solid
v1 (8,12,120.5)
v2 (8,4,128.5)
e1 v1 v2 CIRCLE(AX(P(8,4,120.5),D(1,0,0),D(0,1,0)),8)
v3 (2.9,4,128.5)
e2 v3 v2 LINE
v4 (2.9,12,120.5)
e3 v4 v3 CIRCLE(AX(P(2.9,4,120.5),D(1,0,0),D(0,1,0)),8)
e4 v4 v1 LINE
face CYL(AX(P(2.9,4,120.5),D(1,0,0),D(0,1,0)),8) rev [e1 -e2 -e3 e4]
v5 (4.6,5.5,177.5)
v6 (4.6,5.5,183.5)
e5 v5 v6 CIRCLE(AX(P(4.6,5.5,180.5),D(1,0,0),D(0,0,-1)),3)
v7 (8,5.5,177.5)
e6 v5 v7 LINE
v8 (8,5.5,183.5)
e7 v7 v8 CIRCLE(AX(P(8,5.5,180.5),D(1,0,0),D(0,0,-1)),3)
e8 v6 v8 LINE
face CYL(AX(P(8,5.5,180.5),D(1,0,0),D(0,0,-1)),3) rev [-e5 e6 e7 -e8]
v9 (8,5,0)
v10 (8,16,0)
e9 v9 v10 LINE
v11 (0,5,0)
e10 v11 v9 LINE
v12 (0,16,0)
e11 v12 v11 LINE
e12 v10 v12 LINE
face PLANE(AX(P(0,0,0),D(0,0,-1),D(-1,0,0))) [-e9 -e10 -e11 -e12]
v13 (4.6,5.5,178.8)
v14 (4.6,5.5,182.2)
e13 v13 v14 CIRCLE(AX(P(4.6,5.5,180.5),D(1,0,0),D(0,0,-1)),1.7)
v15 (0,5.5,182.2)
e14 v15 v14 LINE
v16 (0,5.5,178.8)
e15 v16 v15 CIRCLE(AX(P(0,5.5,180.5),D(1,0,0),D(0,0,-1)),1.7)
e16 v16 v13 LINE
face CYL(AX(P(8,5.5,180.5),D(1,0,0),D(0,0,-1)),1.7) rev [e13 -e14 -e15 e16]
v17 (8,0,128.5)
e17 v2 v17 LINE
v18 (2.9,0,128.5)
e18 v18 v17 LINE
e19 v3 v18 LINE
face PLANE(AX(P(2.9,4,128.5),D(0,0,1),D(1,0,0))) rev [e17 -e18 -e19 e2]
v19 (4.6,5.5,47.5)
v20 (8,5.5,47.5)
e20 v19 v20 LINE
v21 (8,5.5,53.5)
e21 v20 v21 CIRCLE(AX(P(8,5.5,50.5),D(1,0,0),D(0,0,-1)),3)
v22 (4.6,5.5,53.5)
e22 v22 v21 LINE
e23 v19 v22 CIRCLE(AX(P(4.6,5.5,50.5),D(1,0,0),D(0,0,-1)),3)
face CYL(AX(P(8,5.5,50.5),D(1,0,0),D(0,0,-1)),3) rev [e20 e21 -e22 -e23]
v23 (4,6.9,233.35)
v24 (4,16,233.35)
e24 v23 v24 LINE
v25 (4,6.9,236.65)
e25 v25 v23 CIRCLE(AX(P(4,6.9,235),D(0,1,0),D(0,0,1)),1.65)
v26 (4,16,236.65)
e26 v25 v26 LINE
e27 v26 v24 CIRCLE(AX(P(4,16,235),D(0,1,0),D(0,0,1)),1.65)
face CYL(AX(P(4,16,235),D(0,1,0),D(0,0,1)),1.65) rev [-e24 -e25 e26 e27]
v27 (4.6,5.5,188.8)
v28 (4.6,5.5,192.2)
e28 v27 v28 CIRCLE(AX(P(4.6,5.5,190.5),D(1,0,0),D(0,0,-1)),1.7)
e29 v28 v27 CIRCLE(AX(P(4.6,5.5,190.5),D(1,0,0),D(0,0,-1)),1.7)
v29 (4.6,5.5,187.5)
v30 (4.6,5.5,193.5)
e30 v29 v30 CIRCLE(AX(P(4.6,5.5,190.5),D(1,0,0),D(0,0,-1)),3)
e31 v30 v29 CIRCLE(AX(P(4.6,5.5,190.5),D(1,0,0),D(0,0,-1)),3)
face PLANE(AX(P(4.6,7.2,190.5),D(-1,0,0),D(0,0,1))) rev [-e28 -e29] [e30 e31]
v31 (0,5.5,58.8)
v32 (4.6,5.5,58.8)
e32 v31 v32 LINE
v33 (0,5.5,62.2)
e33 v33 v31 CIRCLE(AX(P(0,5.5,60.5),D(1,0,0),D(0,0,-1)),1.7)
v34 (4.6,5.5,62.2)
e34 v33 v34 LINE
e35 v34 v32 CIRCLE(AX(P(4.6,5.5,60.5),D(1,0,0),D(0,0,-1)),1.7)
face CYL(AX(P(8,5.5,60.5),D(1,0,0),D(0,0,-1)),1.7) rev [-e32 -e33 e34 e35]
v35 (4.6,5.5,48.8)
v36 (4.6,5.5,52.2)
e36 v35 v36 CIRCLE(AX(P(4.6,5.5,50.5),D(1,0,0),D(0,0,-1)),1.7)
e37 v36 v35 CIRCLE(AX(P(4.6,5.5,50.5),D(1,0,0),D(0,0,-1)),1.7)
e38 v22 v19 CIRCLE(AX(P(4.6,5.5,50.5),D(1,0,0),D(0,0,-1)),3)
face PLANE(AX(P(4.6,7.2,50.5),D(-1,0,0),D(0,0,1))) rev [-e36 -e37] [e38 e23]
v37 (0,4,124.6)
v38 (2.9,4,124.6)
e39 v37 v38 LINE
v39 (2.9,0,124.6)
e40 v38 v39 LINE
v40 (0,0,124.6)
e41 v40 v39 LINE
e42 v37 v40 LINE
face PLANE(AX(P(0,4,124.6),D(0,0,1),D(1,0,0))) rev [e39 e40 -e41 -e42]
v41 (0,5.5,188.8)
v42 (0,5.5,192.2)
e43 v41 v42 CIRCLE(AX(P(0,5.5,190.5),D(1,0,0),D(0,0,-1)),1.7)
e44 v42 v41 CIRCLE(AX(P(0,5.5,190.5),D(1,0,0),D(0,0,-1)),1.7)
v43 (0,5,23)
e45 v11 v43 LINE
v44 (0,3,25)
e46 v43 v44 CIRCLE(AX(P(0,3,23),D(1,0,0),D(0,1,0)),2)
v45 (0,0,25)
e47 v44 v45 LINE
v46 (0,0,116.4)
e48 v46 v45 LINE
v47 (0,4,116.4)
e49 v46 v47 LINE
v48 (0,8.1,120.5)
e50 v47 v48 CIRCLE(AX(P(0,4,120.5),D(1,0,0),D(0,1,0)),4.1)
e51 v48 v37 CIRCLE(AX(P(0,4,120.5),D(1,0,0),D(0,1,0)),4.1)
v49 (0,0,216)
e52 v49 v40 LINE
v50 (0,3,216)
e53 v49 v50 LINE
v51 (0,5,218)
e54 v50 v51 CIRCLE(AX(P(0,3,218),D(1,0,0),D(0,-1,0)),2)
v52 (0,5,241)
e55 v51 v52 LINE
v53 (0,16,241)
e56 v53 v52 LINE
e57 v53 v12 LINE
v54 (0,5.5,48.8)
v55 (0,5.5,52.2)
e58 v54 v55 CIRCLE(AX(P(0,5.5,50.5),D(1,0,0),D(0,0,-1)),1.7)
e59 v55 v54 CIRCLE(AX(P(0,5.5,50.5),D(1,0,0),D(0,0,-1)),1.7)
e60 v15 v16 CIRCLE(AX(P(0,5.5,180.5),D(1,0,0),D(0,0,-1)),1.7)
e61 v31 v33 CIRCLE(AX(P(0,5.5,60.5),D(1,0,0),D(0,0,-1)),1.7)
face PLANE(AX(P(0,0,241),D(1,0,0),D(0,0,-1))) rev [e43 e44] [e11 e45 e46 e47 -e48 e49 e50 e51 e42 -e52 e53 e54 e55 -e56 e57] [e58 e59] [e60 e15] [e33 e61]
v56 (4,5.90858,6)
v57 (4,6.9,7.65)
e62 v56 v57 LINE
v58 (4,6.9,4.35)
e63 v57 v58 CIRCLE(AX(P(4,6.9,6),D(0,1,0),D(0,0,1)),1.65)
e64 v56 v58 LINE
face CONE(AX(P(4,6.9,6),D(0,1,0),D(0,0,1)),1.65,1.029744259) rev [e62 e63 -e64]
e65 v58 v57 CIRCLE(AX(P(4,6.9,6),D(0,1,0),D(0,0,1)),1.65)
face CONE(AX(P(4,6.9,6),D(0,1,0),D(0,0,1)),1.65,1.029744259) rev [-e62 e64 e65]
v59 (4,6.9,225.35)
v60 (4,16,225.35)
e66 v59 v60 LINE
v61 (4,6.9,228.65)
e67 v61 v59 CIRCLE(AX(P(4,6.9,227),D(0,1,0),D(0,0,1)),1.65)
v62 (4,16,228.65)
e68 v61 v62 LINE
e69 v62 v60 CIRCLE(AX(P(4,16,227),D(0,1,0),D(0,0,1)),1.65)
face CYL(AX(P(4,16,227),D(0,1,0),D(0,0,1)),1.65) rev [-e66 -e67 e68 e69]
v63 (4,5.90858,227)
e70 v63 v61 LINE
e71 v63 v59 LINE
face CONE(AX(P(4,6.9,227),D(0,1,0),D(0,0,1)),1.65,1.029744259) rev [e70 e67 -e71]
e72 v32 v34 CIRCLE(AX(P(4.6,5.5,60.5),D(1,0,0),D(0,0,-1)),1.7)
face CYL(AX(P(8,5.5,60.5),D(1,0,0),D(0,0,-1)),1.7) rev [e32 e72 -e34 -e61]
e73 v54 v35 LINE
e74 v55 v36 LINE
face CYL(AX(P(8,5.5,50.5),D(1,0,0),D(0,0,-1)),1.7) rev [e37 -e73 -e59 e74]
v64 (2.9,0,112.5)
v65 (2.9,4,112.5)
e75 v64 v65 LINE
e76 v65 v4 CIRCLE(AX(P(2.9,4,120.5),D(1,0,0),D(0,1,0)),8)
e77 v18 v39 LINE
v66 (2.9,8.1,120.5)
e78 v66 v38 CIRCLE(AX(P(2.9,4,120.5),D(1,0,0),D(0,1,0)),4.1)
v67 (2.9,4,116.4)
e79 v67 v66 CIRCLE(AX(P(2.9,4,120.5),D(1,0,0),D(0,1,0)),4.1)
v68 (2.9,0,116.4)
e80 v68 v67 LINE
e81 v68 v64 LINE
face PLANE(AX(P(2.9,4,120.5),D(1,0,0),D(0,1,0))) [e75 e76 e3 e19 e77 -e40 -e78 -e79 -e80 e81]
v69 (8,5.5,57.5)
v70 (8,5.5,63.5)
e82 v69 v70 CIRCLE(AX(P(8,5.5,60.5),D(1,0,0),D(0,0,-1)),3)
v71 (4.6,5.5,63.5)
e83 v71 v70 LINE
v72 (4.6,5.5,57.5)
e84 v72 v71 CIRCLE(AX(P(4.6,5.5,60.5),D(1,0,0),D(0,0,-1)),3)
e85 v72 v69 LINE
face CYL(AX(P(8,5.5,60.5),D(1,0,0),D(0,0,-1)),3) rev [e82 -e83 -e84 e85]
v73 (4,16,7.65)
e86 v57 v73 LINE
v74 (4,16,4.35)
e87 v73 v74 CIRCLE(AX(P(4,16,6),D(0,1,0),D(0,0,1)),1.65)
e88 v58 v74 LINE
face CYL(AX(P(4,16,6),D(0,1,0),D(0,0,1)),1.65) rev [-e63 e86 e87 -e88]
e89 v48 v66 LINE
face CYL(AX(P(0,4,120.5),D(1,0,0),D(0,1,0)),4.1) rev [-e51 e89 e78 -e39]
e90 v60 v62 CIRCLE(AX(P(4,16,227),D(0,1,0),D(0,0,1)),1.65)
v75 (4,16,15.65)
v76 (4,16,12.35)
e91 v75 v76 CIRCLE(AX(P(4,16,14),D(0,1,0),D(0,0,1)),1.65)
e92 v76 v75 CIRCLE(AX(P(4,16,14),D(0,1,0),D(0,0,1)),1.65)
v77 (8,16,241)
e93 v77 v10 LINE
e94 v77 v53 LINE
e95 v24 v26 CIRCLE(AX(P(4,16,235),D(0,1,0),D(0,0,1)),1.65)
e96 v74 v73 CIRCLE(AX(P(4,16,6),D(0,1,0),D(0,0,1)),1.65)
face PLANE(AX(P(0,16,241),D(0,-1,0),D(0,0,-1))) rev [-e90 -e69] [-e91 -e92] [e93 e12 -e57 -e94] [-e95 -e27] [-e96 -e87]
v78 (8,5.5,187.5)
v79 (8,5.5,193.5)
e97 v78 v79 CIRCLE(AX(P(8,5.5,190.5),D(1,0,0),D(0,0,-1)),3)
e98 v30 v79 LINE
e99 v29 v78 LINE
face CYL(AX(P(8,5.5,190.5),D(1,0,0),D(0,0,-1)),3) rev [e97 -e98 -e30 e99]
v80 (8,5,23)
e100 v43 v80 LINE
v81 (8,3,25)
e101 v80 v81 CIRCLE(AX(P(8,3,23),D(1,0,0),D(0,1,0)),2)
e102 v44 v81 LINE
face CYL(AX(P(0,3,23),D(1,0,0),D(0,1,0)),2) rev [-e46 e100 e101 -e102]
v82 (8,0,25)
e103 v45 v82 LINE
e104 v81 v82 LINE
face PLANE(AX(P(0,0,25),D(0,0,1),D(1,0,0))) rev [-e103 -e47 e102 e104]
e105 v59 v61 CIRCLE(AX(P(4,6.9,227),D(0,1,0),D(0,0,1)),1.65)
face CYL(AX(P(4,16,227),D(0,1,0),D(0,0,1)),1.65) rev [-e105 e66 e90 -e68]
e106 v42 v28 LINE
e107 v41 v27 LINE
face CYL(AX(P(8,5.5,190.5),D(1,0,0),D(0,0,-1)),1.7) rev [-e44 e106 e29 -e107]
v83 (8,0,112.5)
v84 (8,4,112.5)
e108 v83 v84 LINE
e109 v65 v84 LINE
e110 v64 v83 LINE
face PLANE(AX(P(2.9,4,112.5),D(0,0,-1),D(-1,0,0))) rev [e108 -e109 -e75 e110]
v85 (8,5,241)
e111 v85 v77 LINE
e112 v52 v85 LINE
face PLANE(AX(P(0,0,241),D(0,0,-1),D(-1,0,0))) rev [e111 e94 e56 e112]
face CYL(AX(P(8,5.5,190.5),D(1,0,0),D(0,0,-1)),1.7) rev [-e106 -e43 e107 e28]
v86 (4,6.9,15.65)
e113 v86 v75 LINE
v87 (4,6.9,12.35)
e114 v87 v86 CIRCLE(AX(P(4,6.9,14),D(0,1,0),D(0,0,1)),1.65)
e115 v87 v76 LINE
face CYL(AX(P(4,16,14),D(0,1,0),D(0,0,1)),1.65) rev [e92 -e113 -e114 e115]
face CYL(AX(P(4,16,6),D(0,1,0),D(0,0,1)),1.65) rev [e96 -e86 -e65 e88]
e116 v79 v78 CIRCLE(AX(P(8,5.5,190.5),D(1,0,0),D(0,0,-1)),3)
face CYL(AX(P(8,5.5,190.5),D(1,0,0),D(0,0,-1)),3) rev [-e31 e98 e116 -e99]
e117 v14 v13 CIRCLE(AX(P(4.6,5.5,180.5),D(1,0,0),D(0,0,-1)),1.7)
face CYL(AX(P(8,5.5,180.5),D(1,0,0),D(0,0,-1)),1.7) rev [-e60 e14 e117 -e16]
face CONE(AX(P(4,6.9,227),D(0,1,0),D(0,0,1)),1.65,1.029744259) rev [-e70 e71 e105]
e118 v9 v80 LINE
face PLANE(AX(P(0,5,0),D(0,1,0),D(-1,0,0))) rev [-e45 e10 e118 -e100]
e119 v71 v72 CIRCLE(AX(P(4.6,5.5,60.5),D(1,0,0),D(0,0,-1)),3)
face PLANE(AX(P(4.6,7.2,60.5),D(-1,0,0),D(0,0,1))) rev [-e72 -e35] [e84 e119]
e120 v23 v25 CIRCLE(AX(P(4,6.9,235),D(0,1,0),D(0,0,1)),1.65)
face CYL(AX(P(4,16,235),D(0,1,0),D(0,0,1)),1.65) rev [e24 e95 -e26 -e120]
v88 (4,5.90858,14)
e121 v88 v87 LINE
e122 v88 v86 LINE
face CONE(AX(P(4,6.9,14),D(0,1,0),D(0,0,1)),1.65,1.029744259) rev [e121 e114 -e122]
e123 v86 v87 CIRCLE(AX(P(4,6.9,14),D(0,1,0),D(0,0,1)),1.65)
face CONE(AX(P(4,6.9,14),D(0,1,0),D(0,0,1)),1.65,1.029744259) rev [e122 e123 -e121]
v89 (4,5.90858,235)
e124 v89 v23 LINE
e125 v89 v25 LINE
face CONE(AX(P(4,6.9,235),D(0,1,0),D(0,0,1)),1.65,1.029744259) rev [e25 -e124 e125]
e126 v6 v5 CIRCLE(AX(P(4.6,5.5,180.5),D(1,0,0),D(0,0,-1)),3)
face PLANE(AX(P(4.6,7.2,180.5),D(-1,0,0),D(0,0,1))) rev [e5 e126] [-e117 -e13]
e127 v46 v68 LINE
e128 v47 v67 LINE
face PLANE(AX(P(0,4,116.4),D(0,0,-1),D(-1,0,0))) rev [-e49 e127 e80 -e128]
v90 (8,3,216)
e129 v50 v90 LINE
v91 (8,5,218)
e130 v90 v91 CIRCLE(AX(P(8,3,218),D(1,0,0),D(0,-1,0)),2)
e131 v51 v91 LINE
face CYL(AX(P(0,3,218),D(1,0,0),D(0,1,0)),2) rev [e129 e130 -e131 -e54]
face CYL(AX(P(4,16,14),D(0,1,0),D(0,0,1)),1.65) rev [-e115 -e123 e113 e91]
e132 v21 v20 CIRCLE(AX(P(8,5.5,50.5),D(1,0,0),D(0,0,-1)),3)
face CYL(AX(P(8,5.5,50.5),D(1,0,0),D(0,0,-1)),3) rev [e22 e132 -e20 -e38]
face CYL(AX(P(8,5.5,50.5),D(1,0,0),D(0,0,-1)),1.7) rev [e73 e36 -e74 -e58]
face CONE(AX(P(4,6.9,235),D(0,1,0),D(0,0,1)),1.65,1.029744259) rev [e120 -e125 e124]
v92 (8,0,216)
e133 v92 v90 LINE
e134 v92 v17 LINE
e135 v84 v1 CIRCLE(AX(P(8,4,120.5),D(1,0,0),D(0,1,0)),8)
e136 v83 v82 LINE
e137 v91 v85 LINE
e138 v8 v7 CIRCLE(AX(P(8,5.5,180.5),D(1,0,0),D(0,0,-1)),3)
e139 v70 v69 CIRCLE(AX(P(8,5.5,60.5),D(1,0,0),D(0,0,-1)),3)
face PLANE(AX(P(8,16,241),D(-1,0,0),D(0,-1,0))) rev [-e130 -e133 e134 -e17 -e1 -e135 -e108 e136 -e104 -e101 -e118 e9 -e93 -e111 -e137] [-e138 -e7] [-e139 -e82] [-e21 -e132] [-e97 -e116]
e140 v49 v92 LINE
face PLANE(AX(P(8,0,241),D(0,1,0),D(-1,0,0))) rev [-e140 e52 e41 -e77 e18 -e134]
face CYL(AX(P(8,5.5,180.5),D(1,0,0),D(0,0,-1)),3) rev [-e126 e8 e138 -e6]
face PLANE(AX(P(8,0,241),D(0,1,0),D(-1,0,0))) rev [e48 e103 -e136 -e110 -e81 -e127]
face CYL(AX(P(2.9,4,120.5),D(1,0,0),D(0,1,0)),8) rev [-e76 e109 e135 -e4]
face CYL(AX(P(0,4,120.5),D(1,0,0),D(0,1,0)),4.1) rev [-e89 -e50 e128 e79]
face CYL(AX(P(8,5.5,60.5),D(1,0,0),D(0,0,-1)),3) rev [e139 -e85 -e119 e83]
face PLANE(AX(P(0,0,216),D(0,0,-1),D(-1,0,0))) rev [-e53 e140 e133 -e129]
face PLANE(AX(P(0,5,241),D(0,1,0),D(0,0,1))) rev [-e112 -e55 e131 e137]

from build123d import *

# Parameters (mm, degrees)
SKETCH3_W                                            = 8
SKETCH3_H                                            = 16
BOSS_EXTRUDE2_DEPTH                                  = 241
CUT_EXTRUDE1_DEPTH                                   = 5.1
CUT_EXTRUDE2_DEPTH                                   = 242.584374495
CBORE_FOR_M3_HEXAGON_SOCKET_HEAD_CAP_SCR_D           = 3.4
CBORE_FOR_M3_HEXAGON_SOCKET_HEAD_CAP_SCR_DEPTH       = 10.1
CBORE_FOR_M3_HEXAGON_SOCKET_HEAD_CAP_SCR_CBORE_D     = 6
CBORE_FOR_M3_HEXAGON_SOCKET_HEAD_CAP_SCR_CBORE_DEPTH = 3.4
CBORE_FOR_M3_HEXAGON_SOCKET_HEAD_CAP_SCR_TIP         = 1.021463052
M4_TAPPED_HOLE1_D                                    = 3.3
M4_TAPPED_HOLE1_DEPTH                                = 9.1
M4_TAPPED_HOLE1_TIP                                  = 0.991420021
CUT_EXTRUDE3_DEPTH                                   = 242.662988478


with BuildPart() as part:
    # Sketch3 → Boss-Extrude2 (new body)
    with BuildSketch(Plane.XY):
        with Locations((4, 8)):
            Rectangle(SKETCH3_W, SKETCH3_H)
    extrude(amount=BOSS_EXTRUDE2_DEPTH)

    # Sketch4 → Cut-Extrude1 (cut)
    with BuildSketch(Plane(origin=(8, 0, 0), x_dir=(0, 0, -1), z_dir=(1, 0, 0))):
        with BuildLine():
            Line((-112.5, 4), (-112.5, 0))
            ThreePointArc((-112.5, 0), (-120.5, -8), (-128.5, 0))
            Line((-128.5, 0), (-128.5, 4))
            ThreePointArc((-128.5, 4), (-120.5, 12), (-112.5, 4))
        make_face()
    extrude(amount=-CUT_EXTRUDE1_DEPTH, mode=Mode.SUBTRACT)

    # Sketch5 → Cut-Extrude2 (cut, through all)
    with BuildSketch(Plane(origin=(2.9, 0, 0), x_dir=(0, 0, -1), z_dir=(1, 0, 0))):
        with BuildLine():
            Line((-116.4, 4), (-116.4, 0))
            ThreePointArc((-116.4, 0), (-120.5, -4.1), (-124.6, 0))
            Line((-124.6, 0), (-124.6, 4))
            ThreePointArc((-124.6, 4), (-120.5, 8.1), (-116.4, 4))
        make_face()
    extrude(amount=-CUT_EXTRUDE2_DEPTH, mode=Mode.SUBTRACT)

    # CBORE for M3 Hexagon socket head cap screws1
    with Locations(Plane(origin=(8, 0, 0), x_dir=(0, 0, -1), z_dir=(1, 0, 0))):
        with Locations((-60.5, 5.5), (-50.5, 5.5), (-190.5, 5.5), (-180.5, 5.5)):
            CounterBoreHole(CBORE_FOR_M3_HEXAGON_SOCKET_HEAD_CAP_SCR_D / 2, CBORE_FOR_M3_HEXAGON_SOCKET_HEAD_CAP_SCR_CBORE_D / 2, CBORE_FOR_M3_HEXAGON_SOCKET_HEAD_CAP_SCR_CBORE_DEPTH, depth=CBORE_FOR_M3_HEXAGON_SOCKET_HEAD_CAP_SCR_DEPTH)
            with Locations((0, 0, -(CBORE_FOR_M3_HEXAGON_SOCKET_HEAD_CAP_SCR_DEPTH + CBORE_FOR_M3_HEXAGON_SOCKET_HEAD_CAP_SCR_TIP / 2))):  # 118° drill point
                Cone(0, CBORE_FOR_M3_HEXAGON_SOCKET_HEAD_CAP_SCR_D / 2, CBORE_FOR_M3_HEXAGON_SOCKET_HEAD_CAP_SCR_TIP, mode=Mode.SUBTRACT)

    # M4 Tapped Hole1
    with Locations(Plane(origin=(0, 16, 0), x_dir=(1, 0, 0), z_dir=(0, 1, 0))):
        with Locations((4, -235), (4, -227), (4, -14), (4, -6)):
            Hole(M4_TAPPED_HOLE1_D / 2, depth=M4_TAPPED_HOLE1_DEPTH)
            with Locations((0, 0, -(M4_TAPPED_HOLE1_DEPTH + M4_TAPPED_HOLE1_TIP / 2))):  # 118° drill point
                Cone(0, M4_TAPPED_HOLE1_D / 2, M4_TAPPED_HOLE1_TIP, mode=Mode.SUBTRACT)

    # Sketch10 → Cut-Extrude3 (cut, through all)
    with BuildSketch(Plane(origin=(8, 0, 0), x_dir=(0, 0, -1), z_dir=(1, 0, 0))):
        with BuildLine():
            Line((0, 0), (-25, 0))
            Line((-25, 0), (-25, 3))
            ThreePointArc((-25, 3), (-24.414213562, 4.414213562), (-23, 5))
            Line((-23, 5), (0, 5))
            Line((0, 5), (0, 0))
        make_face()
        with BuildLine():
            Line((-216, 0), (-216, 3))
            ThreePointArc((-216, 3), (-216.585786438, 4.414213562), (-218, 5))
            Line((-218, 5), (-241, 5))
            Line((-241, 5), (-241, 0))
            Line((-241, 0), (-216, 0))
        make_face()
    extrude(amount=-CUT_EXTRUDE3_DEPTH, mode=Mode.SUBTRACT)


solid = part.part
